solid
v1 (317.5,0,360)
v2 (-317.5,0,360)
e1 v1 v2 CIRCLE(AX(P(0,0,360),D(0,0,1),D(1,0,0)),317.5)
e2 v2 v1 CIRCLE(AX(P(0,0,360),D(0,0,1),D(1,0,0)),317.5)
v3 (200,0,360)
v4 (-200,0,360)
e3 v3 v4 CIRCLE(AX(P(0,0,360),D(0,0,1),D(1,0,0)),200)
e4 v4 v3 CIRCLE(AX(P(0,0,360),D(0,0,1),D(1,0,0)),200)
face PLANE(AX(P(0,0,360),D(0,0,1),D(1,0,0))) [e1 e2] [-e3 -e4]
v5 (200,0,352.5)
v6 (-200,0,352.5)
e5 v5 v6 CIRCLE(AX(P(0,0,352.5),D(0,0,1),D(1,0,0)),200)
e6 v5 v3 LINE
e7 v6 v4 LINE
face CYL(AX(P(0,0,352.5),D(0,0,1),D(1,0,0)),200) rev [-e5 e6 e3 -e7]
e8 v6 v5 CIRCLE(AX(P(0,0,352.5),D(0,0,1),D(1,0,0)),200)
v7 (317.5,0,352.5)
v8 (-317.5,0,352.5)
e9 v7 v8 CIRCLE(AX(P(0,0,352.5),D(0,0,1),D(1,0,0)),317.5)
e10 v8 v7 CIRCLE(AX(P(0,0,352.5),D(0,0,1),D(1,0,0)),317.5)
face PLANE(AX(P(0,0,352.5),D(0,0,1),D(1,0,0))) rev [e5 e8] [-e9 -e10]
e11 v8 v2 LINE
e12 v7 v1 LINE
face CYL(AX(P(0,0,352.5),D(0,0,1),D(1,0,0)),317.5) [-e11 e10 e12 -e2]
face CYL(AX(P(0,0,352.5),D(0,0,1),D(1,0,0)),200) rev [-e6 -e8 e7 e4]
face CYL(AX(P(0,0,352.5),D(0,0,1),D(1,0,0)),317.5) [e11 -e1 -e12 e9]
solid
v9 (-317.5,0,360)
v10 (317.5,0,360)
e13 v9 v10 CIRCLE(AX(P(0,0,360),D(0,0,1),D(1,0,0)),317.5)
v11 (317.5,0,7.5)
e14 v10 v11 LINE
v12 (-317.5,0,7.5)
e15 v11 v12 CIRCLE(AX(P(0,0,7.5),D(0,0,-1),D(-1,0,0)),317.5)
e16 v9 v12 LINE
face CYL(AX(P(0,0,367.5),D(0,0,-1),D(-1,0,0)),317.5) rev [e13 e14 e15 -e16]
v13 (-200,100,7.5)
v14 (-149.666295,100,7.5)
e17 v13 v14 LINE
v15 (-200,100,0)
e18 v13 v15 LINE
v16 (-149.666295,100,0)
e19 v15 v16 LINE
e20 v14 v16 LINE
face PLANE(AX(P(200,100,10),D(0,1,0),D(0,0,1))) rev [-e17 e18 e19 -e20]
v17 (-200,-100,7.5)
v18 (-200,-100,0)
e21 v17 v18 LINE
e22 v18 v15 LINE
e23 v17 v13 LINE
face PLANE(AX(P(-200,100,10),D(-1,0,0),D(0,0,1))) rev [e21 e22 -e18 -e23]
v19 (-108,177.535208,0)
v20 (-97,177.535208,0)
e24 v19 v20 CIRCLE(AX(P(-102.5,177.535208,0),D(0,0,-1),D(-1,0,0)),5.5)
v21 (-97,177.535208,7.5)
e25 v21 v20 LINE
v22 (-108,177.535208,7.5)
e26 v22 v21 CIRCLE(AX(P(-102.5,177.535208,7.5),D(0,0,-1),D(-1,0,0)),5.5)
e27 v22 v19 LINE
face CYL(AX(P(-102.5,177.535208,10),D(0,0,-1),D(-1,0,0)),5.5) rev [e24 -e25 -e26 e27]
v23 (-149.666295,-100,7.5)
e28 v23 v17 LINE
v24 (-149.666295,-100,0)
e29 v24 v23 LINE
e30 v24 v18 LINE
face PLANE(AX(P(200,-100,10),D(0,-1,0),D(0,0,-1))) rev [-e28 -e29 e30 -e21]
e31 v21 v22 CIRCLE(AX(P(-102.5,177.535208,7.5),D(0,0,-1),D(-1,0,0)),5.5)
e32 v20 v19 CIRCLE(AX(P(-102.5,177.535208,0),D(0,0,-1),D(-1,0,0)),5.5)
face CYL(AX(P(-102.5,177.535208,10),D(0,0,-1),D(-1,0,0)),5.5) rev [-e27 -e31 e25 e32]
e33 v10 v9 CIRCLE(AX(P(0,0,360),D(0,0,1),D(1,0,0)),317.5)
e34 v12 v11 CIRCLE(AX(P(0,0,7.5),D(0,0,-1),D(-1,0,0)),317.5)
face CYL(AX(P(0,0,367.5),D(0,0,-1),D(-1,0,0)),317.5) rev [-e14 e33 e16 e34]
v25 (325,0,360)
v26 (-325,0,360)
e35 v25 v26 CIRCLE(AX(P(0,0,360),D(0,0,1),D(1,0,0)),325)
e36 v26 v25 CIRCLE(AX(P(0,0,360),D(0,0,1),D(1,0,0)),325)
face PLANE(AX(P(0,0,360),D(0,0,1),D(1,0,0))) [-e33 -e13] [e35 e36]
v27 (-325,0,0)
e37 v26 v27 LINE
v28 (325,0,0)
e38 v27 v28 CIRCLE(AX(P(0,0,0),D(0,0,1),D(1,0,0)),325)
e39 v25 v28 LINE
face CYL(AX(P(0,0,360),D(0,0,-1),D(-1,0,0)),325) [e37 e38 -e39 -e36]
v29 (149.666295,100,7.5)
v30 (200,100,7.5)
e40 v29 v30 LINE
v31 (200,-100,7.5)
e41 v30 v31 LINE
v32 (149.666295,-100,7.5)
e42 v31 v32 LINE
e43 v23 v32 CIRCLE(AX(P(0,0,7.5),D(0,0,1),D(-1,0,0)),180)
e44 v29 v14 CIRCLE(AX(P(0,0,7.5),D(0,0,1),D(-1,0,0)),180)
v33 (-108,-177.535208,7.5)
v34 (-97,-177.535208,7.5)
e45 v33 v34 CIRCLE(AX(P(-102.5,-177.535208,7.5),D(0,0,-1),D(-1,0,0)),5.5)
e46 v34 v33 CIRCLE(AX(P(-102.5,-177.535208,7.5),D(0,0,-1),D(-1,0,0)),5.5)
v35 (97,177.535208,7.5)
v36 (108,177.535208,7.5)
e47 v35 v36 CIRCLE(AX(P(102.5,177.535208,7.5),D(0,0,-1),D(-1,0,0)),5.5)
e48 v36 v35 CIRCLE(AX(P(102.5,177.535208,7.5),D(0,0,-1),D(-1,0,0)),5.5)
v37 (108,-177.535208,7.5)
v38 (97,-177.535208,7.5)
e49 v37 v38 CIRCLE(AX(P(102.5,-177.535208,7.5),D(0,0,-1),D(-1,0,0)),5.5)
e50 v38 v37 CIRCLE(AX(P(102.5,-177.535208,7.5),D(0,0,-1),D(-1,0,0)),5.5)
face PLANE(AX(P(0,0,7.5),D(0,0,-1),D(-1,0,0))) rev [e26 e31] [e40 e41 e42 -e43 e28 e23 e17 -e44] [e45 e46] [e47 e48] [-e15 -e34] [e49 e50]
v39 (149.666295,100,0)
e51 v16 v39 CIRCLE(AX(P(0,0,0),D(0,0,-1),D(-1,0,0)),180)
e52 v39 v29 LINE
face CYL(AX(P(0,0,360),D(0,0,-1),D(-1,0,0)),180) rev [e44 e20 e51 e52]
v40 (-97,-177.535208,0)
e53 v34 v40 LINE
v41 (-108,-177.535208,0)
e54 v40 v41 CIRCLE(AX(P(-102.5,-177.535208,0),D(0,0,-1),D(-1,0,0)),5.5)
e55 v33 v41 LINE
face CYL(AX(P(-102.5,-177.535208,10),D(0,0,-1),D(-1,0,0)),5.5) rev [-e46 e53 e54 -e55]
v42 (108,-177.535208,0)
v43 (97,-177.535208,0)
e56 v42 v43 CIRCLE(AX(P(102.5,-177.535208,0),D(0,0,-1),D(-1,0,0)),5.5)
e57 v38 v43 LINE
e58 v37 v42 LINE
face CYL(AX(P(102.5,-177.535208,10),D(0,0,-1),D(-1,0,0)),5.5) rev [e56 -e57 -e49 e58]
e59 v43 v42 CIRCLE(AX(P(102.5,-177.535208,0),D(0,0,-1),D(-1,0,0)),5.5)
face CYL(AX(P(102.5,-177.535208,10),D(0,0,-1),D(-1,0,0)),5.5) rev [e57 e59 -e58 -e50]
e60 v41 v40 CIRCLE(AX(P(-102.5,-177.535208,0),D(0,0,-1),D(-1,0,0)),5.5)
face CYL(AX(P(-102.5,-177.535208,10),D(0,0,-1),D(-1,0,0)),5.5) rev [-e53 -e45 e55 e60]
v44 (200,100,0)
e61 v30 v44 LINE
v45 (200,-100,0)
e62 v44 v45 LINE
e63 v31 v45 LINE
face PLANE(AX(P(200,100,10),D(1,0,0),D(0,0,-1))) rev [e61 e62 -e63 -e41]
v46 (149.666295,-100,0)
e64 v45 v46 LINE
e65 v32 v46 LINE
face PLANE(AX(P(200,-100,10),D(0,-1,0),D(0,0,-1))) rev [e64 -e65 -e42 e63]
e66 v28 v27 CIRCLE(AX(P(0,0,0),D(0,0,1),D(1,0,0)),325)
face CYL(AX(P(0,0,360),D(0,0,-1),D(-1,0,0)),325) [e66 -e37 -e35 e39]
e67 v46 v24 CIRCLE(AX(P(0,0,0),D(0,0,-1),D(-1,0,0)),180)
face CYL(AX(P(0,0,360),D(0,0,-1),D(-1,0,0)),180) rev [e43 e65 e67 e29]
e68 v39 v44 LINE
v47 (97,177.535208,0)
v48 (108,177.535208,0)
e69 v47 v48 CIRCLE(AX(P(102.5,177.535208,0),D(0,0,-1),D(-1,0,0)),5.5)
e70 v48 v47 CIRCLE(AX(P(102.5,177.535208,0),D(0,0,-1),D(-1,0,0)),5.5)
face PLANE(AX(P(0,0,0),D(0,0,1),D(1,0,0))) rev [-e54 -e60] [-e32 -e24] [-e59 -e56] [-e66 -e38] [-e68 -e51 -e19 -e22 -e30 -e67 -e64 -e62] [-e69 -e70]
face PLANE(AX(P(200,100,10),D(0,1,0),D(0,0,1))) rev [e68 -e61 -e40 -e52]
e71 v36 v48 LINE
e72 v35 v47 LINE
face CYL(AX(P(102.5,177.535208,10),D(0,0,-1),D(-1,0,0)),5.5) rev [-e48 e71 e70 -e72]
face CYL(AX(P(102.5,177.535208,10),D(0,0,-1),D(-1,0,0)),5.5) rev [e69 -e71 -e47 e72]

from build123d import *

# Parameters (mm, degrees)
SKETCH1_R           = 325
BOSS_EXTRUDE1_DEPTH = 360
SKETCH2_R           = 180
CUT_EXTRUDE1_DEPTH  = 584.823603497
CUT_EXTRUDE2_START  = -7.5
SKETCH3_R           = 317.5
CUT_EXTRUDE2_DEPTH  = 360
SKETCH4_R           = 5.5
SKETCH4_W           = 400
SKETCH4_H           = 200
CUT_EXTRUDE3_DEPTH  = 10
SKETCH5_R           = 317.5
SKETCH5_R_2         = 200
BOSS_EXTRUDE2_DEPTH = 7.5


with BuildPart() as part:
    # Sketch1 → Boss-Extrude1 (new body)
    with BuildSketch(Plane.XY):
        with Locations(Location((0, 0, 0), (0, 0, 180))):
            Circle(SKETCH1_R)
    extrude(amount=BOSS_EXTRUDE1_DEPTH)

    # Sketch2 → Cut-Extrude1 (cut, through all)
    with BuildSketch(Plane(origin=(0, 0, 0), x_dir=(-1, 0, 0), z_dir=(0, 0, -1))):
        Circle(SKETCH2_R)
    extrude(amount=-CUT_EXTRUDE1_DEPTH, mode=Mode.SUBTRACT)

    # Sketch3 → Cut-Extrude2 (cut)
    with BuildSketch(Plane(origin=(0, 0, 0), x_dir=(-1, 0, 0), z_dir=(0, 0, -1)).offset(CUT_EXTRUDE2_START)):
        Circle(SKETCH3_R)
    extrude(amount=-CUT_EXTRUDE2_DEPTH, mode=Mode.SUBTRACT)

    # Sketch4 → Cut-Extrude3 (cut)
    with BuildSketch(Plane(origin=(0, 0, 0), x_dir=(-1, 0, 0), z_dir=(0, 0, -1))):
        with Locations((-102.5, 177.535207776)):
            Circle(SKETCH4_R)
        with Locations((102.5, 177.535207776)):
            Circle(SKETCH4_R)
        with Locations((102.5, -177.535207776)):
            Circle(SKETCH4_R)
        with Locations((-102.5, -177.535207776)):
            Circle(SKETCH4_R)
        Rectangle(SKETCH4_W, SKETCH4_H)
    extrude(amount=-CUT_EXTRUDE3_DEPTH, mode=Mode.SUBTRACT)


with BuildPart() as body_2:
    # Sketch5 → Boss-Extrude2 (new body)
    with BuildSketch(Plane.XY.offset(360)):
        Circle(SKETCH5_R)
        Circle(SKETCH5_R_2, mode=Mode.SUBTRACT)
    extrude(amount=-BOSS_EXTRUDE2_DEPTH)


solid = Compound([part.part, body_2.part])
